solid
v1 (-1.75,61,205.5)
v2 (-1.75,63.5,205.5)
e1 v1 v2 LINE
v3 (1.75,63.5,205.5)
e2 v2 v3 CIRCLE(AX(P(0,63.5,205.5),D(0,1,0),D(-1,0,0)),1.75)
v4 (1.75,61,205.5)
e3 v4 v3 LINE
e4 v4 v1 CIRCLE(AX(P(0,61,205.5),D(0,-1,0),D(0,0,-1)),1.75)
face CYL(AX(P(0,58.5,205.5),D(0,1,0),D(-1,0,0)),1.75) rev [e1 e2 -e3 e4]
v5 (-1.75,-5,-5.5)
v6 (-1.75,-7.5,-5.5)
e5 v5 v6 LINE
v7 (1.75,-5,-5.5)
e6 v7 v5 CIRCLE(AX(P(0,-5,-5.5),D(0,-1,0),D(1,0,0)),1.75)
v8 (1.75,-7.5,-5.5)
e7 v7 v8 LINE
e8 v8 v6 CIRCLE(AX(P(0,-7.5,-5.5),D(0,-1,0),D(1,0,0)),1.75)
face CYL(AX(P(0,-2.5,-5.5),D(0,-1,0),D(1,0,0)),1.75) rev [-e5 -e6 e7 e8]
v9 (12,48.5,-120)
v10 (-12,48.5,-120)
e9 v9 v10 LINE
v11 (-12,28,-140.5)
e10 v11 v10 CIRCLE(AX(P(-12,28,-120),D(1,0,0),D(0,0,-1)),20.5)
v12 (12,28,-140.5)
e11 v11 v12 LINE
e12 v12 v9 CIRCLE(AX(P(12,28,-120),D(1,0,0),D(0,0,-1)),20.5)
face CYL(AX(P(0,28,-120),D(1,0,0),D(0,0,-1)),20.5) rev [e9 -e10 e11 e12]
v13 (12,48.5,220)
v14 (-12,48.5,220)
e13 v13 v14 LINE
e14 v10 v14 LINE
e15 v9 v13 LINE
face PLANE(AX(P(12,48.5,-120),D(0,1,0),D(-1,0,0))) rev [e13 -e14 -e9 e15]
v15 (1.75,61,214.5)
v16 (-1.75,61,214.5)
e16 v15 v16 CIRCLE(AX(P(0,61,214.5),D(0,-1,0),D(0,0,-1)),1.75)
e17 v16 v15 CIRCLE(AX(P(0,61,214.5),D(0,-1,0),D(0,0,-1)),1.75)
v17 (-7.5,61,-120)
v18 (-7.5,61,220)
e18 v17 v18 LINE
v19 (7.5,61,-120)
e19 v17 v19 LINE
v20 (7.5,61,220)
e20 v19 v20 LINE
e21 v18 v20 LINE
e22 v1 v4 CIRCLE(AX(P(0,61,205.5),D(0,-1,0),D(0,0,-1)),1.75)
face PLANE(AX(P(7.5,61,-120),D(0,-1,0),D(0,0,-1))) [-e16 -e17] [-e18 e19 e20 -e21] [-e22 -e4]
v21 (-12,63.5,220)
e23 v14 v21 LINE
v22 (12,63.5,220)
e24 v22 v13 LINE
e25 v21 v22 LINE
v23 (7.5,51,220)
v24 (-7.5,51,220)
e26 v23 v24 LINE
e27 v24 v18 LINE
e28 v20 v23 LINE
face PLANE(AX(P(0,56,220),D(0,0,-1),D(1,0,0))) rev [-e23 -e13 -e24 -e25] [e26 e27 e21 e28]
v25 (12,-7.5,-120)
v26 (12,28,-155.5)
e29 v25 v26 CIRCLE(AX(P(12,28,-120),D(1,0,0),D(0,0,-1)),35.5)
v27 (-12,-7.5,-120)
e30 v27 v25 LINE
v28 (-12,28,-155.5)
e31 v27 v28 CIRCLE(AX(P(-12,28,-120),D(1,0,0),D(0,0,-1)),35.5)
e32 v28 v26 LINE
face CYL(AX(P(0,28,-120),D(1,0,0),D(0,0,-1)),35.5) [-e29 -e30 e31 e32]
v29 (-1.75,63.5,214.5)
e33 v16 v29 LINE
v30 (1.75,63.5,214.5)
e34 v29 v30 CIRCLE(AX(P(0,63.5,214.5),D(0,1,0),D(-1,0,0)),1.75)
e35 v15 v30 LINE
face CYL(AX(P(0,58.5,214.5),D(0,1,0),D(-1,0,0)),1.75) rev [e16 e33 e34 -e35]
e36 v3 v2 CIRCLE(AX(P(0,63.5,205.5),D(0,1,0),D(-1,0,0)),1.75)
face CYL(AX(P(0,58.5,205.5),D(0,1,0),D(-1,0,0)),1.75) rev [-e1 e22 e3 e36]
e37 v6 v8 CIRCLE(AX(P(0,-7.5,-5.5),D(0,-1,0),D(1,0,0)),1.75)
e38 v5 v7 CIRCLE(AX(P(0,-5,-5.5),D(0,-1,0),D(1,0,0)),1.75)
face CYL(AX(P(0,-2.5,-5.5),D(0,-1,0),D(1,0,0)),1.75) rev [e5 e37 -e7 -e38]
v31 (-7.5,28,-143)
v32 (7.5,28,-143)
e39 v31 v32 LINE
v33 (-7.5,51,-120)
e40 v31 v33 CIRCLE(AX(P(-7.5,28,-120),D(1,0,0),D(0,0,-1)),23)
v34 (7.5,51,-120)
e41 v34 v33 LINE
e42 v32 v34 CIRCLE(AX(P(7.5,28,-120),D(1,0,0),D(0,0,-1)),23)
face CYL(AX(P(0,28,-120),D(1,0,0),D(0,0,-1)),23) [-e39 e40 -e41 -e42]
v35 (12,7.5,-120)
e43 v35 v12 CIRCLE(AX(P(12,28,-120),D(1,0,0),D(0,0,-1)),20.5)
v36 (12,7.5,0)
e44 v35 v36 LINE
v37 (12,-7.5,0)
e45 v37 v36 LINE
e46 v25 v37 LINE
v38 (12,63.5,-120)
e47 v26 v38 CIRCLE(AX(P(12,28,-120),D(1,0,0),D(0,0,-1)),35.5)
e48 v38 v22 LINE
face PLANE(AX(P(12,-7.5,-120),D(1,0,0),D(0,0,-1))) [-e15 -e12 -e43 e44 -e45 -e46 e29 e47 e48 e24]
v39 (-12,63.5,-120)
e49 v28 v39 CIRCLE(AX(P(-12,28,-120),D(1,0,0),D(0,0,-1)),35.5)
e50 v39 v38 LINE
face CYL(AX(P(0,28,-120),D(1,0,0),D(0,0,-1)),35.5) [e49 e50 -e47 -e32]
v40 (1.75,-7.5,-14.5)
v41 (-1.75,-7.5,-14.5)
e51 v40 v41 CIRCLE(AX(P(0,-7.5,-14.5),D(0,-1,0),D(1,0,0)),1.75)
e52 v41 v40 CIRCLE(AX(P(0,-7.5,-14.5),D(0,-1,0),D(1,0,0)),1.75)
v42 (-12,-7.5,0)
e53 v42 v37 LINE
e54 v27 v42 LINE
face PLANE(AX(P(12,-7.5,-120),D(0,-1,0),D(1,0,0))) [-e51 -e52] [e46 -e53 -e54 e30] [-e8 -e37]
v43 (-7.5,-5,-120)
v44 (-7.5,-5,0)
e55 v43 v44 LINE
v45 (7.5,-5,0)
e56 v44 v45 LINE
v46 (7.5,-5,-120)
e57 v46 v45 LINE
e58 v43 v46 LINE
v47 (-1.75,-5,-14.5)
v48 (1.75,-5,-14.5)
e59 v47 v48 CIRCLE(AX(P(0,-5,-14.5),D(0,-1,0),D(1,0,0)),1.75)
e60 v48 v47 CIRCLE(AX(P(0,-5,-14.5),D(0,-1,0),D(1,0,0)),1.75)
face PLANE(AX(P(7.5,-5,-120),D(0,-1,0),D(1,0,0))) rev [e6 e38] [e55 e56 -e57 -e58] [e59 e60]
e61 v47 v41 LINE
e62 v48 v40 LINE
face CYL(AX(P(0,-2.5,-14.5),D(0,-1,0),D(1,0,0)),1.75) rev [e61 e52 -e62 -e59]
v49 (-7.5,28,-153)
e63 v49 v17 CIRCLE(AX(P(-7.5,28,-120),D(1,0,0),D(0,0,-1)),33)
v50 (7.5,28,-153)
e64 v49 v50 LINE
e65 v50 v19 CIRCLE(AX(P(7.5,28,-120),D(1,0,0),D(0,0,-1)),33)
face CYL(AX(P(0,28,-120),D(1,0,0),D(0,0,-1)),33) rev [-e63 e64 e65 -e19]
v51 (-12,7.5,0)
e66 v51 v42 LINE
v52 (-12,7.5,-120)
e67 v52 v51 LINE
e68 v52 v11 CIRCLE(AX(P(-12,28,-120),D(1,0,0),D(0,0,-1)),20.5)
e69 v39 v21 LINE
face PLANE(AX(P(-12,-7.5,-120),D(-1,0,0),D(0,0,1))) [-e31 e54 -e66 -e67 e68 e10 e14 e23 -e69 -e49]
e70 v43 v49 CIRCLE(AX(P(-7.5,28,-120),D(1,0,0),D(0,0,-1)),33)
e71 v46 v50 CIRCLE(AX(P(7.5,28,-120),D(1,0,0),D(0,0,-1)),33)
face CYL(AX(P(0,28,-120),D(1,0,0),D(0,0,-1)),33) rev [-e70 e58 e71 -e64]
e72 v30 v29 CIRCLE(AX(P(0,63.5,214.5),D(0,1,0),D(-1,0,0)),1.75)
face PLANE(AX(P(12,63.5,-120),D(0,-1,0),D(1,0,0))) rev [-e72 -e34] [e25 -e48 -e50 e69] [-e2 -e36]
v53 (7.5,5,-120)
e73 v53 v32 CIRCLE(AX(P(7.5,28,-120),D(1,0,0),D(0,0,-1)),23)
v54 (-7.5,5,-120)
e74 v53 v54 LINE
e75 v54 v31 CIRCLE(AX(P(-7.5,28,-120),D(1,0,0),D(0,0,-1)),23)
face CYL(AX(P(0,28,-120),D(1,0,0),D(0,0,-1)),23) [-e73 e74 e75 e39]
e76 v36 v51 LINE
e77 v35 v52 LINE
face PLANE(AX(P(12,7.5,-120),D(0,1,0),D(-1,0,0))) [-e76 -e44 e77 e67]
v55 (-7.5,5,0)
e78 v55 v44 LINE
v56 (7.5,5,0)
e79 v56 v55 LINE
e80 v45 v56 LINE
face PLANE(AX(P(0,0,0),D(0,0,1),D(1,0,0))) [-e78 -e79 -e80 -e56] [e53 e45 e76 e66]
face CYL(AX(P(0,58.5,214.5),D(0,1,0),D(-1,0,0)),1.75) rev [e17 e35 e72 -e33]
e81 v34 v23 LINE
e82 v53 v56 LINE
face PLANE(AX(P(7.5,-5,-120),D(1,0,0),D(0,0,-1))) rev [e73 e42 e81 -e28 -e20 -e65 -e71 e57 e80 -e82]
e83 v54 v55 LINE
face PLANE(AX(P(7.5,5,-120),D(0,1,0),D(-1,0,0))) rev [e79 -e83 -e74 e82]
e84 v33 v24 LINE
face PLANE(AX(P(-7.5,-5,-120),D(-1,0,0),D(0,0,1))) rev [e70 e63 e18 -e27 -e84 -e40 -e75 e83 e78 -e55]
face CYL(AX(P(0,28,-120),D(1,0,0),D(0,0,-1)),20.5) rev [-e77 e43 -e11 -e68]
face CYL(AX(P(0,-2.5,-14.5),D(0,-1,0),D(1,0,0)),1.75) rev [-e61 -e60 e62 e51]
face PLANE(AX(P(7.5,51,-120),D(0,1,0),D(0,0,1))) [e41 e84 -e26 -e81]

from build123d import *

# Parameters (mm, degrees)
SKETCH_1_W          = 24
SKETCH_1_H          = 15
SKETCH_1_W_2        = 15
SKETCH_1_H_2        = 10
SKETCH_3_R          = 1.75
CUT_EXTRUDE_1_DEPTH = 5
SKETCH_4_R          = 1.75
CUT_EXTRUDE_2_DEPTH = 5


with BuildPart() as part:
    # 扫描1: sweep along a path in 草图2
    with BuildLine(Plane(origin=(0, 0, 0), x_dir=(0, 0, -1), z_dir=(1, 0, 0))) as sweep_1_path:
        Line((0, 0), (120, 0))
        ThreePointArc((120, 0), (148, 28), (120, 56))
        Line((120, 56), (-220, 56))
    # 草图1 → 扫描1 (sweep)
    with BuildSketch(Plane.XY):
        Rectangle(SKETCH_1_W, SKETCH_1_H)
        Rectangle(SKETCH_1_W_2, SKETCH_1_H_2, mode=Mode.SUBTRACT)
    sweep(path=sweep_1_path.line)

    # 草图3 → 切除-拉伸1 (cut)
    with BuildSketch(Plane(origin=(0, 63.5, 0), x_dir=(1, 0, 0), z_dir=(0, 1, 0))):
        with Locations(Location((0, -214.5, 0), (0, 0, 180))):
            Circle(SKETCH_3_R)
        with Locations(Location((0, -205.5, 0), (0, 0, 180))):
            Circle(SKETCH_3_R)
    extrude(amount=-CUT_EXTRUDE_1_DEPTH, mode=Mode.SUBTRACT)

    # 草图4 → 切除-拉伸2 (cut)
    with BuildSketch(Plane.XZ.offset(7.5)):
        with Locations((0, -5.5)):
            Circle(SKETCH_4_R)
        with Locations((0, -14.5)):
            Circle(SKETCH_4_R)
    extrude(amount=-CUT_EXTRUDE_2_DEPTH, mode=Mode.SUBTRACT)


solid = part.part
